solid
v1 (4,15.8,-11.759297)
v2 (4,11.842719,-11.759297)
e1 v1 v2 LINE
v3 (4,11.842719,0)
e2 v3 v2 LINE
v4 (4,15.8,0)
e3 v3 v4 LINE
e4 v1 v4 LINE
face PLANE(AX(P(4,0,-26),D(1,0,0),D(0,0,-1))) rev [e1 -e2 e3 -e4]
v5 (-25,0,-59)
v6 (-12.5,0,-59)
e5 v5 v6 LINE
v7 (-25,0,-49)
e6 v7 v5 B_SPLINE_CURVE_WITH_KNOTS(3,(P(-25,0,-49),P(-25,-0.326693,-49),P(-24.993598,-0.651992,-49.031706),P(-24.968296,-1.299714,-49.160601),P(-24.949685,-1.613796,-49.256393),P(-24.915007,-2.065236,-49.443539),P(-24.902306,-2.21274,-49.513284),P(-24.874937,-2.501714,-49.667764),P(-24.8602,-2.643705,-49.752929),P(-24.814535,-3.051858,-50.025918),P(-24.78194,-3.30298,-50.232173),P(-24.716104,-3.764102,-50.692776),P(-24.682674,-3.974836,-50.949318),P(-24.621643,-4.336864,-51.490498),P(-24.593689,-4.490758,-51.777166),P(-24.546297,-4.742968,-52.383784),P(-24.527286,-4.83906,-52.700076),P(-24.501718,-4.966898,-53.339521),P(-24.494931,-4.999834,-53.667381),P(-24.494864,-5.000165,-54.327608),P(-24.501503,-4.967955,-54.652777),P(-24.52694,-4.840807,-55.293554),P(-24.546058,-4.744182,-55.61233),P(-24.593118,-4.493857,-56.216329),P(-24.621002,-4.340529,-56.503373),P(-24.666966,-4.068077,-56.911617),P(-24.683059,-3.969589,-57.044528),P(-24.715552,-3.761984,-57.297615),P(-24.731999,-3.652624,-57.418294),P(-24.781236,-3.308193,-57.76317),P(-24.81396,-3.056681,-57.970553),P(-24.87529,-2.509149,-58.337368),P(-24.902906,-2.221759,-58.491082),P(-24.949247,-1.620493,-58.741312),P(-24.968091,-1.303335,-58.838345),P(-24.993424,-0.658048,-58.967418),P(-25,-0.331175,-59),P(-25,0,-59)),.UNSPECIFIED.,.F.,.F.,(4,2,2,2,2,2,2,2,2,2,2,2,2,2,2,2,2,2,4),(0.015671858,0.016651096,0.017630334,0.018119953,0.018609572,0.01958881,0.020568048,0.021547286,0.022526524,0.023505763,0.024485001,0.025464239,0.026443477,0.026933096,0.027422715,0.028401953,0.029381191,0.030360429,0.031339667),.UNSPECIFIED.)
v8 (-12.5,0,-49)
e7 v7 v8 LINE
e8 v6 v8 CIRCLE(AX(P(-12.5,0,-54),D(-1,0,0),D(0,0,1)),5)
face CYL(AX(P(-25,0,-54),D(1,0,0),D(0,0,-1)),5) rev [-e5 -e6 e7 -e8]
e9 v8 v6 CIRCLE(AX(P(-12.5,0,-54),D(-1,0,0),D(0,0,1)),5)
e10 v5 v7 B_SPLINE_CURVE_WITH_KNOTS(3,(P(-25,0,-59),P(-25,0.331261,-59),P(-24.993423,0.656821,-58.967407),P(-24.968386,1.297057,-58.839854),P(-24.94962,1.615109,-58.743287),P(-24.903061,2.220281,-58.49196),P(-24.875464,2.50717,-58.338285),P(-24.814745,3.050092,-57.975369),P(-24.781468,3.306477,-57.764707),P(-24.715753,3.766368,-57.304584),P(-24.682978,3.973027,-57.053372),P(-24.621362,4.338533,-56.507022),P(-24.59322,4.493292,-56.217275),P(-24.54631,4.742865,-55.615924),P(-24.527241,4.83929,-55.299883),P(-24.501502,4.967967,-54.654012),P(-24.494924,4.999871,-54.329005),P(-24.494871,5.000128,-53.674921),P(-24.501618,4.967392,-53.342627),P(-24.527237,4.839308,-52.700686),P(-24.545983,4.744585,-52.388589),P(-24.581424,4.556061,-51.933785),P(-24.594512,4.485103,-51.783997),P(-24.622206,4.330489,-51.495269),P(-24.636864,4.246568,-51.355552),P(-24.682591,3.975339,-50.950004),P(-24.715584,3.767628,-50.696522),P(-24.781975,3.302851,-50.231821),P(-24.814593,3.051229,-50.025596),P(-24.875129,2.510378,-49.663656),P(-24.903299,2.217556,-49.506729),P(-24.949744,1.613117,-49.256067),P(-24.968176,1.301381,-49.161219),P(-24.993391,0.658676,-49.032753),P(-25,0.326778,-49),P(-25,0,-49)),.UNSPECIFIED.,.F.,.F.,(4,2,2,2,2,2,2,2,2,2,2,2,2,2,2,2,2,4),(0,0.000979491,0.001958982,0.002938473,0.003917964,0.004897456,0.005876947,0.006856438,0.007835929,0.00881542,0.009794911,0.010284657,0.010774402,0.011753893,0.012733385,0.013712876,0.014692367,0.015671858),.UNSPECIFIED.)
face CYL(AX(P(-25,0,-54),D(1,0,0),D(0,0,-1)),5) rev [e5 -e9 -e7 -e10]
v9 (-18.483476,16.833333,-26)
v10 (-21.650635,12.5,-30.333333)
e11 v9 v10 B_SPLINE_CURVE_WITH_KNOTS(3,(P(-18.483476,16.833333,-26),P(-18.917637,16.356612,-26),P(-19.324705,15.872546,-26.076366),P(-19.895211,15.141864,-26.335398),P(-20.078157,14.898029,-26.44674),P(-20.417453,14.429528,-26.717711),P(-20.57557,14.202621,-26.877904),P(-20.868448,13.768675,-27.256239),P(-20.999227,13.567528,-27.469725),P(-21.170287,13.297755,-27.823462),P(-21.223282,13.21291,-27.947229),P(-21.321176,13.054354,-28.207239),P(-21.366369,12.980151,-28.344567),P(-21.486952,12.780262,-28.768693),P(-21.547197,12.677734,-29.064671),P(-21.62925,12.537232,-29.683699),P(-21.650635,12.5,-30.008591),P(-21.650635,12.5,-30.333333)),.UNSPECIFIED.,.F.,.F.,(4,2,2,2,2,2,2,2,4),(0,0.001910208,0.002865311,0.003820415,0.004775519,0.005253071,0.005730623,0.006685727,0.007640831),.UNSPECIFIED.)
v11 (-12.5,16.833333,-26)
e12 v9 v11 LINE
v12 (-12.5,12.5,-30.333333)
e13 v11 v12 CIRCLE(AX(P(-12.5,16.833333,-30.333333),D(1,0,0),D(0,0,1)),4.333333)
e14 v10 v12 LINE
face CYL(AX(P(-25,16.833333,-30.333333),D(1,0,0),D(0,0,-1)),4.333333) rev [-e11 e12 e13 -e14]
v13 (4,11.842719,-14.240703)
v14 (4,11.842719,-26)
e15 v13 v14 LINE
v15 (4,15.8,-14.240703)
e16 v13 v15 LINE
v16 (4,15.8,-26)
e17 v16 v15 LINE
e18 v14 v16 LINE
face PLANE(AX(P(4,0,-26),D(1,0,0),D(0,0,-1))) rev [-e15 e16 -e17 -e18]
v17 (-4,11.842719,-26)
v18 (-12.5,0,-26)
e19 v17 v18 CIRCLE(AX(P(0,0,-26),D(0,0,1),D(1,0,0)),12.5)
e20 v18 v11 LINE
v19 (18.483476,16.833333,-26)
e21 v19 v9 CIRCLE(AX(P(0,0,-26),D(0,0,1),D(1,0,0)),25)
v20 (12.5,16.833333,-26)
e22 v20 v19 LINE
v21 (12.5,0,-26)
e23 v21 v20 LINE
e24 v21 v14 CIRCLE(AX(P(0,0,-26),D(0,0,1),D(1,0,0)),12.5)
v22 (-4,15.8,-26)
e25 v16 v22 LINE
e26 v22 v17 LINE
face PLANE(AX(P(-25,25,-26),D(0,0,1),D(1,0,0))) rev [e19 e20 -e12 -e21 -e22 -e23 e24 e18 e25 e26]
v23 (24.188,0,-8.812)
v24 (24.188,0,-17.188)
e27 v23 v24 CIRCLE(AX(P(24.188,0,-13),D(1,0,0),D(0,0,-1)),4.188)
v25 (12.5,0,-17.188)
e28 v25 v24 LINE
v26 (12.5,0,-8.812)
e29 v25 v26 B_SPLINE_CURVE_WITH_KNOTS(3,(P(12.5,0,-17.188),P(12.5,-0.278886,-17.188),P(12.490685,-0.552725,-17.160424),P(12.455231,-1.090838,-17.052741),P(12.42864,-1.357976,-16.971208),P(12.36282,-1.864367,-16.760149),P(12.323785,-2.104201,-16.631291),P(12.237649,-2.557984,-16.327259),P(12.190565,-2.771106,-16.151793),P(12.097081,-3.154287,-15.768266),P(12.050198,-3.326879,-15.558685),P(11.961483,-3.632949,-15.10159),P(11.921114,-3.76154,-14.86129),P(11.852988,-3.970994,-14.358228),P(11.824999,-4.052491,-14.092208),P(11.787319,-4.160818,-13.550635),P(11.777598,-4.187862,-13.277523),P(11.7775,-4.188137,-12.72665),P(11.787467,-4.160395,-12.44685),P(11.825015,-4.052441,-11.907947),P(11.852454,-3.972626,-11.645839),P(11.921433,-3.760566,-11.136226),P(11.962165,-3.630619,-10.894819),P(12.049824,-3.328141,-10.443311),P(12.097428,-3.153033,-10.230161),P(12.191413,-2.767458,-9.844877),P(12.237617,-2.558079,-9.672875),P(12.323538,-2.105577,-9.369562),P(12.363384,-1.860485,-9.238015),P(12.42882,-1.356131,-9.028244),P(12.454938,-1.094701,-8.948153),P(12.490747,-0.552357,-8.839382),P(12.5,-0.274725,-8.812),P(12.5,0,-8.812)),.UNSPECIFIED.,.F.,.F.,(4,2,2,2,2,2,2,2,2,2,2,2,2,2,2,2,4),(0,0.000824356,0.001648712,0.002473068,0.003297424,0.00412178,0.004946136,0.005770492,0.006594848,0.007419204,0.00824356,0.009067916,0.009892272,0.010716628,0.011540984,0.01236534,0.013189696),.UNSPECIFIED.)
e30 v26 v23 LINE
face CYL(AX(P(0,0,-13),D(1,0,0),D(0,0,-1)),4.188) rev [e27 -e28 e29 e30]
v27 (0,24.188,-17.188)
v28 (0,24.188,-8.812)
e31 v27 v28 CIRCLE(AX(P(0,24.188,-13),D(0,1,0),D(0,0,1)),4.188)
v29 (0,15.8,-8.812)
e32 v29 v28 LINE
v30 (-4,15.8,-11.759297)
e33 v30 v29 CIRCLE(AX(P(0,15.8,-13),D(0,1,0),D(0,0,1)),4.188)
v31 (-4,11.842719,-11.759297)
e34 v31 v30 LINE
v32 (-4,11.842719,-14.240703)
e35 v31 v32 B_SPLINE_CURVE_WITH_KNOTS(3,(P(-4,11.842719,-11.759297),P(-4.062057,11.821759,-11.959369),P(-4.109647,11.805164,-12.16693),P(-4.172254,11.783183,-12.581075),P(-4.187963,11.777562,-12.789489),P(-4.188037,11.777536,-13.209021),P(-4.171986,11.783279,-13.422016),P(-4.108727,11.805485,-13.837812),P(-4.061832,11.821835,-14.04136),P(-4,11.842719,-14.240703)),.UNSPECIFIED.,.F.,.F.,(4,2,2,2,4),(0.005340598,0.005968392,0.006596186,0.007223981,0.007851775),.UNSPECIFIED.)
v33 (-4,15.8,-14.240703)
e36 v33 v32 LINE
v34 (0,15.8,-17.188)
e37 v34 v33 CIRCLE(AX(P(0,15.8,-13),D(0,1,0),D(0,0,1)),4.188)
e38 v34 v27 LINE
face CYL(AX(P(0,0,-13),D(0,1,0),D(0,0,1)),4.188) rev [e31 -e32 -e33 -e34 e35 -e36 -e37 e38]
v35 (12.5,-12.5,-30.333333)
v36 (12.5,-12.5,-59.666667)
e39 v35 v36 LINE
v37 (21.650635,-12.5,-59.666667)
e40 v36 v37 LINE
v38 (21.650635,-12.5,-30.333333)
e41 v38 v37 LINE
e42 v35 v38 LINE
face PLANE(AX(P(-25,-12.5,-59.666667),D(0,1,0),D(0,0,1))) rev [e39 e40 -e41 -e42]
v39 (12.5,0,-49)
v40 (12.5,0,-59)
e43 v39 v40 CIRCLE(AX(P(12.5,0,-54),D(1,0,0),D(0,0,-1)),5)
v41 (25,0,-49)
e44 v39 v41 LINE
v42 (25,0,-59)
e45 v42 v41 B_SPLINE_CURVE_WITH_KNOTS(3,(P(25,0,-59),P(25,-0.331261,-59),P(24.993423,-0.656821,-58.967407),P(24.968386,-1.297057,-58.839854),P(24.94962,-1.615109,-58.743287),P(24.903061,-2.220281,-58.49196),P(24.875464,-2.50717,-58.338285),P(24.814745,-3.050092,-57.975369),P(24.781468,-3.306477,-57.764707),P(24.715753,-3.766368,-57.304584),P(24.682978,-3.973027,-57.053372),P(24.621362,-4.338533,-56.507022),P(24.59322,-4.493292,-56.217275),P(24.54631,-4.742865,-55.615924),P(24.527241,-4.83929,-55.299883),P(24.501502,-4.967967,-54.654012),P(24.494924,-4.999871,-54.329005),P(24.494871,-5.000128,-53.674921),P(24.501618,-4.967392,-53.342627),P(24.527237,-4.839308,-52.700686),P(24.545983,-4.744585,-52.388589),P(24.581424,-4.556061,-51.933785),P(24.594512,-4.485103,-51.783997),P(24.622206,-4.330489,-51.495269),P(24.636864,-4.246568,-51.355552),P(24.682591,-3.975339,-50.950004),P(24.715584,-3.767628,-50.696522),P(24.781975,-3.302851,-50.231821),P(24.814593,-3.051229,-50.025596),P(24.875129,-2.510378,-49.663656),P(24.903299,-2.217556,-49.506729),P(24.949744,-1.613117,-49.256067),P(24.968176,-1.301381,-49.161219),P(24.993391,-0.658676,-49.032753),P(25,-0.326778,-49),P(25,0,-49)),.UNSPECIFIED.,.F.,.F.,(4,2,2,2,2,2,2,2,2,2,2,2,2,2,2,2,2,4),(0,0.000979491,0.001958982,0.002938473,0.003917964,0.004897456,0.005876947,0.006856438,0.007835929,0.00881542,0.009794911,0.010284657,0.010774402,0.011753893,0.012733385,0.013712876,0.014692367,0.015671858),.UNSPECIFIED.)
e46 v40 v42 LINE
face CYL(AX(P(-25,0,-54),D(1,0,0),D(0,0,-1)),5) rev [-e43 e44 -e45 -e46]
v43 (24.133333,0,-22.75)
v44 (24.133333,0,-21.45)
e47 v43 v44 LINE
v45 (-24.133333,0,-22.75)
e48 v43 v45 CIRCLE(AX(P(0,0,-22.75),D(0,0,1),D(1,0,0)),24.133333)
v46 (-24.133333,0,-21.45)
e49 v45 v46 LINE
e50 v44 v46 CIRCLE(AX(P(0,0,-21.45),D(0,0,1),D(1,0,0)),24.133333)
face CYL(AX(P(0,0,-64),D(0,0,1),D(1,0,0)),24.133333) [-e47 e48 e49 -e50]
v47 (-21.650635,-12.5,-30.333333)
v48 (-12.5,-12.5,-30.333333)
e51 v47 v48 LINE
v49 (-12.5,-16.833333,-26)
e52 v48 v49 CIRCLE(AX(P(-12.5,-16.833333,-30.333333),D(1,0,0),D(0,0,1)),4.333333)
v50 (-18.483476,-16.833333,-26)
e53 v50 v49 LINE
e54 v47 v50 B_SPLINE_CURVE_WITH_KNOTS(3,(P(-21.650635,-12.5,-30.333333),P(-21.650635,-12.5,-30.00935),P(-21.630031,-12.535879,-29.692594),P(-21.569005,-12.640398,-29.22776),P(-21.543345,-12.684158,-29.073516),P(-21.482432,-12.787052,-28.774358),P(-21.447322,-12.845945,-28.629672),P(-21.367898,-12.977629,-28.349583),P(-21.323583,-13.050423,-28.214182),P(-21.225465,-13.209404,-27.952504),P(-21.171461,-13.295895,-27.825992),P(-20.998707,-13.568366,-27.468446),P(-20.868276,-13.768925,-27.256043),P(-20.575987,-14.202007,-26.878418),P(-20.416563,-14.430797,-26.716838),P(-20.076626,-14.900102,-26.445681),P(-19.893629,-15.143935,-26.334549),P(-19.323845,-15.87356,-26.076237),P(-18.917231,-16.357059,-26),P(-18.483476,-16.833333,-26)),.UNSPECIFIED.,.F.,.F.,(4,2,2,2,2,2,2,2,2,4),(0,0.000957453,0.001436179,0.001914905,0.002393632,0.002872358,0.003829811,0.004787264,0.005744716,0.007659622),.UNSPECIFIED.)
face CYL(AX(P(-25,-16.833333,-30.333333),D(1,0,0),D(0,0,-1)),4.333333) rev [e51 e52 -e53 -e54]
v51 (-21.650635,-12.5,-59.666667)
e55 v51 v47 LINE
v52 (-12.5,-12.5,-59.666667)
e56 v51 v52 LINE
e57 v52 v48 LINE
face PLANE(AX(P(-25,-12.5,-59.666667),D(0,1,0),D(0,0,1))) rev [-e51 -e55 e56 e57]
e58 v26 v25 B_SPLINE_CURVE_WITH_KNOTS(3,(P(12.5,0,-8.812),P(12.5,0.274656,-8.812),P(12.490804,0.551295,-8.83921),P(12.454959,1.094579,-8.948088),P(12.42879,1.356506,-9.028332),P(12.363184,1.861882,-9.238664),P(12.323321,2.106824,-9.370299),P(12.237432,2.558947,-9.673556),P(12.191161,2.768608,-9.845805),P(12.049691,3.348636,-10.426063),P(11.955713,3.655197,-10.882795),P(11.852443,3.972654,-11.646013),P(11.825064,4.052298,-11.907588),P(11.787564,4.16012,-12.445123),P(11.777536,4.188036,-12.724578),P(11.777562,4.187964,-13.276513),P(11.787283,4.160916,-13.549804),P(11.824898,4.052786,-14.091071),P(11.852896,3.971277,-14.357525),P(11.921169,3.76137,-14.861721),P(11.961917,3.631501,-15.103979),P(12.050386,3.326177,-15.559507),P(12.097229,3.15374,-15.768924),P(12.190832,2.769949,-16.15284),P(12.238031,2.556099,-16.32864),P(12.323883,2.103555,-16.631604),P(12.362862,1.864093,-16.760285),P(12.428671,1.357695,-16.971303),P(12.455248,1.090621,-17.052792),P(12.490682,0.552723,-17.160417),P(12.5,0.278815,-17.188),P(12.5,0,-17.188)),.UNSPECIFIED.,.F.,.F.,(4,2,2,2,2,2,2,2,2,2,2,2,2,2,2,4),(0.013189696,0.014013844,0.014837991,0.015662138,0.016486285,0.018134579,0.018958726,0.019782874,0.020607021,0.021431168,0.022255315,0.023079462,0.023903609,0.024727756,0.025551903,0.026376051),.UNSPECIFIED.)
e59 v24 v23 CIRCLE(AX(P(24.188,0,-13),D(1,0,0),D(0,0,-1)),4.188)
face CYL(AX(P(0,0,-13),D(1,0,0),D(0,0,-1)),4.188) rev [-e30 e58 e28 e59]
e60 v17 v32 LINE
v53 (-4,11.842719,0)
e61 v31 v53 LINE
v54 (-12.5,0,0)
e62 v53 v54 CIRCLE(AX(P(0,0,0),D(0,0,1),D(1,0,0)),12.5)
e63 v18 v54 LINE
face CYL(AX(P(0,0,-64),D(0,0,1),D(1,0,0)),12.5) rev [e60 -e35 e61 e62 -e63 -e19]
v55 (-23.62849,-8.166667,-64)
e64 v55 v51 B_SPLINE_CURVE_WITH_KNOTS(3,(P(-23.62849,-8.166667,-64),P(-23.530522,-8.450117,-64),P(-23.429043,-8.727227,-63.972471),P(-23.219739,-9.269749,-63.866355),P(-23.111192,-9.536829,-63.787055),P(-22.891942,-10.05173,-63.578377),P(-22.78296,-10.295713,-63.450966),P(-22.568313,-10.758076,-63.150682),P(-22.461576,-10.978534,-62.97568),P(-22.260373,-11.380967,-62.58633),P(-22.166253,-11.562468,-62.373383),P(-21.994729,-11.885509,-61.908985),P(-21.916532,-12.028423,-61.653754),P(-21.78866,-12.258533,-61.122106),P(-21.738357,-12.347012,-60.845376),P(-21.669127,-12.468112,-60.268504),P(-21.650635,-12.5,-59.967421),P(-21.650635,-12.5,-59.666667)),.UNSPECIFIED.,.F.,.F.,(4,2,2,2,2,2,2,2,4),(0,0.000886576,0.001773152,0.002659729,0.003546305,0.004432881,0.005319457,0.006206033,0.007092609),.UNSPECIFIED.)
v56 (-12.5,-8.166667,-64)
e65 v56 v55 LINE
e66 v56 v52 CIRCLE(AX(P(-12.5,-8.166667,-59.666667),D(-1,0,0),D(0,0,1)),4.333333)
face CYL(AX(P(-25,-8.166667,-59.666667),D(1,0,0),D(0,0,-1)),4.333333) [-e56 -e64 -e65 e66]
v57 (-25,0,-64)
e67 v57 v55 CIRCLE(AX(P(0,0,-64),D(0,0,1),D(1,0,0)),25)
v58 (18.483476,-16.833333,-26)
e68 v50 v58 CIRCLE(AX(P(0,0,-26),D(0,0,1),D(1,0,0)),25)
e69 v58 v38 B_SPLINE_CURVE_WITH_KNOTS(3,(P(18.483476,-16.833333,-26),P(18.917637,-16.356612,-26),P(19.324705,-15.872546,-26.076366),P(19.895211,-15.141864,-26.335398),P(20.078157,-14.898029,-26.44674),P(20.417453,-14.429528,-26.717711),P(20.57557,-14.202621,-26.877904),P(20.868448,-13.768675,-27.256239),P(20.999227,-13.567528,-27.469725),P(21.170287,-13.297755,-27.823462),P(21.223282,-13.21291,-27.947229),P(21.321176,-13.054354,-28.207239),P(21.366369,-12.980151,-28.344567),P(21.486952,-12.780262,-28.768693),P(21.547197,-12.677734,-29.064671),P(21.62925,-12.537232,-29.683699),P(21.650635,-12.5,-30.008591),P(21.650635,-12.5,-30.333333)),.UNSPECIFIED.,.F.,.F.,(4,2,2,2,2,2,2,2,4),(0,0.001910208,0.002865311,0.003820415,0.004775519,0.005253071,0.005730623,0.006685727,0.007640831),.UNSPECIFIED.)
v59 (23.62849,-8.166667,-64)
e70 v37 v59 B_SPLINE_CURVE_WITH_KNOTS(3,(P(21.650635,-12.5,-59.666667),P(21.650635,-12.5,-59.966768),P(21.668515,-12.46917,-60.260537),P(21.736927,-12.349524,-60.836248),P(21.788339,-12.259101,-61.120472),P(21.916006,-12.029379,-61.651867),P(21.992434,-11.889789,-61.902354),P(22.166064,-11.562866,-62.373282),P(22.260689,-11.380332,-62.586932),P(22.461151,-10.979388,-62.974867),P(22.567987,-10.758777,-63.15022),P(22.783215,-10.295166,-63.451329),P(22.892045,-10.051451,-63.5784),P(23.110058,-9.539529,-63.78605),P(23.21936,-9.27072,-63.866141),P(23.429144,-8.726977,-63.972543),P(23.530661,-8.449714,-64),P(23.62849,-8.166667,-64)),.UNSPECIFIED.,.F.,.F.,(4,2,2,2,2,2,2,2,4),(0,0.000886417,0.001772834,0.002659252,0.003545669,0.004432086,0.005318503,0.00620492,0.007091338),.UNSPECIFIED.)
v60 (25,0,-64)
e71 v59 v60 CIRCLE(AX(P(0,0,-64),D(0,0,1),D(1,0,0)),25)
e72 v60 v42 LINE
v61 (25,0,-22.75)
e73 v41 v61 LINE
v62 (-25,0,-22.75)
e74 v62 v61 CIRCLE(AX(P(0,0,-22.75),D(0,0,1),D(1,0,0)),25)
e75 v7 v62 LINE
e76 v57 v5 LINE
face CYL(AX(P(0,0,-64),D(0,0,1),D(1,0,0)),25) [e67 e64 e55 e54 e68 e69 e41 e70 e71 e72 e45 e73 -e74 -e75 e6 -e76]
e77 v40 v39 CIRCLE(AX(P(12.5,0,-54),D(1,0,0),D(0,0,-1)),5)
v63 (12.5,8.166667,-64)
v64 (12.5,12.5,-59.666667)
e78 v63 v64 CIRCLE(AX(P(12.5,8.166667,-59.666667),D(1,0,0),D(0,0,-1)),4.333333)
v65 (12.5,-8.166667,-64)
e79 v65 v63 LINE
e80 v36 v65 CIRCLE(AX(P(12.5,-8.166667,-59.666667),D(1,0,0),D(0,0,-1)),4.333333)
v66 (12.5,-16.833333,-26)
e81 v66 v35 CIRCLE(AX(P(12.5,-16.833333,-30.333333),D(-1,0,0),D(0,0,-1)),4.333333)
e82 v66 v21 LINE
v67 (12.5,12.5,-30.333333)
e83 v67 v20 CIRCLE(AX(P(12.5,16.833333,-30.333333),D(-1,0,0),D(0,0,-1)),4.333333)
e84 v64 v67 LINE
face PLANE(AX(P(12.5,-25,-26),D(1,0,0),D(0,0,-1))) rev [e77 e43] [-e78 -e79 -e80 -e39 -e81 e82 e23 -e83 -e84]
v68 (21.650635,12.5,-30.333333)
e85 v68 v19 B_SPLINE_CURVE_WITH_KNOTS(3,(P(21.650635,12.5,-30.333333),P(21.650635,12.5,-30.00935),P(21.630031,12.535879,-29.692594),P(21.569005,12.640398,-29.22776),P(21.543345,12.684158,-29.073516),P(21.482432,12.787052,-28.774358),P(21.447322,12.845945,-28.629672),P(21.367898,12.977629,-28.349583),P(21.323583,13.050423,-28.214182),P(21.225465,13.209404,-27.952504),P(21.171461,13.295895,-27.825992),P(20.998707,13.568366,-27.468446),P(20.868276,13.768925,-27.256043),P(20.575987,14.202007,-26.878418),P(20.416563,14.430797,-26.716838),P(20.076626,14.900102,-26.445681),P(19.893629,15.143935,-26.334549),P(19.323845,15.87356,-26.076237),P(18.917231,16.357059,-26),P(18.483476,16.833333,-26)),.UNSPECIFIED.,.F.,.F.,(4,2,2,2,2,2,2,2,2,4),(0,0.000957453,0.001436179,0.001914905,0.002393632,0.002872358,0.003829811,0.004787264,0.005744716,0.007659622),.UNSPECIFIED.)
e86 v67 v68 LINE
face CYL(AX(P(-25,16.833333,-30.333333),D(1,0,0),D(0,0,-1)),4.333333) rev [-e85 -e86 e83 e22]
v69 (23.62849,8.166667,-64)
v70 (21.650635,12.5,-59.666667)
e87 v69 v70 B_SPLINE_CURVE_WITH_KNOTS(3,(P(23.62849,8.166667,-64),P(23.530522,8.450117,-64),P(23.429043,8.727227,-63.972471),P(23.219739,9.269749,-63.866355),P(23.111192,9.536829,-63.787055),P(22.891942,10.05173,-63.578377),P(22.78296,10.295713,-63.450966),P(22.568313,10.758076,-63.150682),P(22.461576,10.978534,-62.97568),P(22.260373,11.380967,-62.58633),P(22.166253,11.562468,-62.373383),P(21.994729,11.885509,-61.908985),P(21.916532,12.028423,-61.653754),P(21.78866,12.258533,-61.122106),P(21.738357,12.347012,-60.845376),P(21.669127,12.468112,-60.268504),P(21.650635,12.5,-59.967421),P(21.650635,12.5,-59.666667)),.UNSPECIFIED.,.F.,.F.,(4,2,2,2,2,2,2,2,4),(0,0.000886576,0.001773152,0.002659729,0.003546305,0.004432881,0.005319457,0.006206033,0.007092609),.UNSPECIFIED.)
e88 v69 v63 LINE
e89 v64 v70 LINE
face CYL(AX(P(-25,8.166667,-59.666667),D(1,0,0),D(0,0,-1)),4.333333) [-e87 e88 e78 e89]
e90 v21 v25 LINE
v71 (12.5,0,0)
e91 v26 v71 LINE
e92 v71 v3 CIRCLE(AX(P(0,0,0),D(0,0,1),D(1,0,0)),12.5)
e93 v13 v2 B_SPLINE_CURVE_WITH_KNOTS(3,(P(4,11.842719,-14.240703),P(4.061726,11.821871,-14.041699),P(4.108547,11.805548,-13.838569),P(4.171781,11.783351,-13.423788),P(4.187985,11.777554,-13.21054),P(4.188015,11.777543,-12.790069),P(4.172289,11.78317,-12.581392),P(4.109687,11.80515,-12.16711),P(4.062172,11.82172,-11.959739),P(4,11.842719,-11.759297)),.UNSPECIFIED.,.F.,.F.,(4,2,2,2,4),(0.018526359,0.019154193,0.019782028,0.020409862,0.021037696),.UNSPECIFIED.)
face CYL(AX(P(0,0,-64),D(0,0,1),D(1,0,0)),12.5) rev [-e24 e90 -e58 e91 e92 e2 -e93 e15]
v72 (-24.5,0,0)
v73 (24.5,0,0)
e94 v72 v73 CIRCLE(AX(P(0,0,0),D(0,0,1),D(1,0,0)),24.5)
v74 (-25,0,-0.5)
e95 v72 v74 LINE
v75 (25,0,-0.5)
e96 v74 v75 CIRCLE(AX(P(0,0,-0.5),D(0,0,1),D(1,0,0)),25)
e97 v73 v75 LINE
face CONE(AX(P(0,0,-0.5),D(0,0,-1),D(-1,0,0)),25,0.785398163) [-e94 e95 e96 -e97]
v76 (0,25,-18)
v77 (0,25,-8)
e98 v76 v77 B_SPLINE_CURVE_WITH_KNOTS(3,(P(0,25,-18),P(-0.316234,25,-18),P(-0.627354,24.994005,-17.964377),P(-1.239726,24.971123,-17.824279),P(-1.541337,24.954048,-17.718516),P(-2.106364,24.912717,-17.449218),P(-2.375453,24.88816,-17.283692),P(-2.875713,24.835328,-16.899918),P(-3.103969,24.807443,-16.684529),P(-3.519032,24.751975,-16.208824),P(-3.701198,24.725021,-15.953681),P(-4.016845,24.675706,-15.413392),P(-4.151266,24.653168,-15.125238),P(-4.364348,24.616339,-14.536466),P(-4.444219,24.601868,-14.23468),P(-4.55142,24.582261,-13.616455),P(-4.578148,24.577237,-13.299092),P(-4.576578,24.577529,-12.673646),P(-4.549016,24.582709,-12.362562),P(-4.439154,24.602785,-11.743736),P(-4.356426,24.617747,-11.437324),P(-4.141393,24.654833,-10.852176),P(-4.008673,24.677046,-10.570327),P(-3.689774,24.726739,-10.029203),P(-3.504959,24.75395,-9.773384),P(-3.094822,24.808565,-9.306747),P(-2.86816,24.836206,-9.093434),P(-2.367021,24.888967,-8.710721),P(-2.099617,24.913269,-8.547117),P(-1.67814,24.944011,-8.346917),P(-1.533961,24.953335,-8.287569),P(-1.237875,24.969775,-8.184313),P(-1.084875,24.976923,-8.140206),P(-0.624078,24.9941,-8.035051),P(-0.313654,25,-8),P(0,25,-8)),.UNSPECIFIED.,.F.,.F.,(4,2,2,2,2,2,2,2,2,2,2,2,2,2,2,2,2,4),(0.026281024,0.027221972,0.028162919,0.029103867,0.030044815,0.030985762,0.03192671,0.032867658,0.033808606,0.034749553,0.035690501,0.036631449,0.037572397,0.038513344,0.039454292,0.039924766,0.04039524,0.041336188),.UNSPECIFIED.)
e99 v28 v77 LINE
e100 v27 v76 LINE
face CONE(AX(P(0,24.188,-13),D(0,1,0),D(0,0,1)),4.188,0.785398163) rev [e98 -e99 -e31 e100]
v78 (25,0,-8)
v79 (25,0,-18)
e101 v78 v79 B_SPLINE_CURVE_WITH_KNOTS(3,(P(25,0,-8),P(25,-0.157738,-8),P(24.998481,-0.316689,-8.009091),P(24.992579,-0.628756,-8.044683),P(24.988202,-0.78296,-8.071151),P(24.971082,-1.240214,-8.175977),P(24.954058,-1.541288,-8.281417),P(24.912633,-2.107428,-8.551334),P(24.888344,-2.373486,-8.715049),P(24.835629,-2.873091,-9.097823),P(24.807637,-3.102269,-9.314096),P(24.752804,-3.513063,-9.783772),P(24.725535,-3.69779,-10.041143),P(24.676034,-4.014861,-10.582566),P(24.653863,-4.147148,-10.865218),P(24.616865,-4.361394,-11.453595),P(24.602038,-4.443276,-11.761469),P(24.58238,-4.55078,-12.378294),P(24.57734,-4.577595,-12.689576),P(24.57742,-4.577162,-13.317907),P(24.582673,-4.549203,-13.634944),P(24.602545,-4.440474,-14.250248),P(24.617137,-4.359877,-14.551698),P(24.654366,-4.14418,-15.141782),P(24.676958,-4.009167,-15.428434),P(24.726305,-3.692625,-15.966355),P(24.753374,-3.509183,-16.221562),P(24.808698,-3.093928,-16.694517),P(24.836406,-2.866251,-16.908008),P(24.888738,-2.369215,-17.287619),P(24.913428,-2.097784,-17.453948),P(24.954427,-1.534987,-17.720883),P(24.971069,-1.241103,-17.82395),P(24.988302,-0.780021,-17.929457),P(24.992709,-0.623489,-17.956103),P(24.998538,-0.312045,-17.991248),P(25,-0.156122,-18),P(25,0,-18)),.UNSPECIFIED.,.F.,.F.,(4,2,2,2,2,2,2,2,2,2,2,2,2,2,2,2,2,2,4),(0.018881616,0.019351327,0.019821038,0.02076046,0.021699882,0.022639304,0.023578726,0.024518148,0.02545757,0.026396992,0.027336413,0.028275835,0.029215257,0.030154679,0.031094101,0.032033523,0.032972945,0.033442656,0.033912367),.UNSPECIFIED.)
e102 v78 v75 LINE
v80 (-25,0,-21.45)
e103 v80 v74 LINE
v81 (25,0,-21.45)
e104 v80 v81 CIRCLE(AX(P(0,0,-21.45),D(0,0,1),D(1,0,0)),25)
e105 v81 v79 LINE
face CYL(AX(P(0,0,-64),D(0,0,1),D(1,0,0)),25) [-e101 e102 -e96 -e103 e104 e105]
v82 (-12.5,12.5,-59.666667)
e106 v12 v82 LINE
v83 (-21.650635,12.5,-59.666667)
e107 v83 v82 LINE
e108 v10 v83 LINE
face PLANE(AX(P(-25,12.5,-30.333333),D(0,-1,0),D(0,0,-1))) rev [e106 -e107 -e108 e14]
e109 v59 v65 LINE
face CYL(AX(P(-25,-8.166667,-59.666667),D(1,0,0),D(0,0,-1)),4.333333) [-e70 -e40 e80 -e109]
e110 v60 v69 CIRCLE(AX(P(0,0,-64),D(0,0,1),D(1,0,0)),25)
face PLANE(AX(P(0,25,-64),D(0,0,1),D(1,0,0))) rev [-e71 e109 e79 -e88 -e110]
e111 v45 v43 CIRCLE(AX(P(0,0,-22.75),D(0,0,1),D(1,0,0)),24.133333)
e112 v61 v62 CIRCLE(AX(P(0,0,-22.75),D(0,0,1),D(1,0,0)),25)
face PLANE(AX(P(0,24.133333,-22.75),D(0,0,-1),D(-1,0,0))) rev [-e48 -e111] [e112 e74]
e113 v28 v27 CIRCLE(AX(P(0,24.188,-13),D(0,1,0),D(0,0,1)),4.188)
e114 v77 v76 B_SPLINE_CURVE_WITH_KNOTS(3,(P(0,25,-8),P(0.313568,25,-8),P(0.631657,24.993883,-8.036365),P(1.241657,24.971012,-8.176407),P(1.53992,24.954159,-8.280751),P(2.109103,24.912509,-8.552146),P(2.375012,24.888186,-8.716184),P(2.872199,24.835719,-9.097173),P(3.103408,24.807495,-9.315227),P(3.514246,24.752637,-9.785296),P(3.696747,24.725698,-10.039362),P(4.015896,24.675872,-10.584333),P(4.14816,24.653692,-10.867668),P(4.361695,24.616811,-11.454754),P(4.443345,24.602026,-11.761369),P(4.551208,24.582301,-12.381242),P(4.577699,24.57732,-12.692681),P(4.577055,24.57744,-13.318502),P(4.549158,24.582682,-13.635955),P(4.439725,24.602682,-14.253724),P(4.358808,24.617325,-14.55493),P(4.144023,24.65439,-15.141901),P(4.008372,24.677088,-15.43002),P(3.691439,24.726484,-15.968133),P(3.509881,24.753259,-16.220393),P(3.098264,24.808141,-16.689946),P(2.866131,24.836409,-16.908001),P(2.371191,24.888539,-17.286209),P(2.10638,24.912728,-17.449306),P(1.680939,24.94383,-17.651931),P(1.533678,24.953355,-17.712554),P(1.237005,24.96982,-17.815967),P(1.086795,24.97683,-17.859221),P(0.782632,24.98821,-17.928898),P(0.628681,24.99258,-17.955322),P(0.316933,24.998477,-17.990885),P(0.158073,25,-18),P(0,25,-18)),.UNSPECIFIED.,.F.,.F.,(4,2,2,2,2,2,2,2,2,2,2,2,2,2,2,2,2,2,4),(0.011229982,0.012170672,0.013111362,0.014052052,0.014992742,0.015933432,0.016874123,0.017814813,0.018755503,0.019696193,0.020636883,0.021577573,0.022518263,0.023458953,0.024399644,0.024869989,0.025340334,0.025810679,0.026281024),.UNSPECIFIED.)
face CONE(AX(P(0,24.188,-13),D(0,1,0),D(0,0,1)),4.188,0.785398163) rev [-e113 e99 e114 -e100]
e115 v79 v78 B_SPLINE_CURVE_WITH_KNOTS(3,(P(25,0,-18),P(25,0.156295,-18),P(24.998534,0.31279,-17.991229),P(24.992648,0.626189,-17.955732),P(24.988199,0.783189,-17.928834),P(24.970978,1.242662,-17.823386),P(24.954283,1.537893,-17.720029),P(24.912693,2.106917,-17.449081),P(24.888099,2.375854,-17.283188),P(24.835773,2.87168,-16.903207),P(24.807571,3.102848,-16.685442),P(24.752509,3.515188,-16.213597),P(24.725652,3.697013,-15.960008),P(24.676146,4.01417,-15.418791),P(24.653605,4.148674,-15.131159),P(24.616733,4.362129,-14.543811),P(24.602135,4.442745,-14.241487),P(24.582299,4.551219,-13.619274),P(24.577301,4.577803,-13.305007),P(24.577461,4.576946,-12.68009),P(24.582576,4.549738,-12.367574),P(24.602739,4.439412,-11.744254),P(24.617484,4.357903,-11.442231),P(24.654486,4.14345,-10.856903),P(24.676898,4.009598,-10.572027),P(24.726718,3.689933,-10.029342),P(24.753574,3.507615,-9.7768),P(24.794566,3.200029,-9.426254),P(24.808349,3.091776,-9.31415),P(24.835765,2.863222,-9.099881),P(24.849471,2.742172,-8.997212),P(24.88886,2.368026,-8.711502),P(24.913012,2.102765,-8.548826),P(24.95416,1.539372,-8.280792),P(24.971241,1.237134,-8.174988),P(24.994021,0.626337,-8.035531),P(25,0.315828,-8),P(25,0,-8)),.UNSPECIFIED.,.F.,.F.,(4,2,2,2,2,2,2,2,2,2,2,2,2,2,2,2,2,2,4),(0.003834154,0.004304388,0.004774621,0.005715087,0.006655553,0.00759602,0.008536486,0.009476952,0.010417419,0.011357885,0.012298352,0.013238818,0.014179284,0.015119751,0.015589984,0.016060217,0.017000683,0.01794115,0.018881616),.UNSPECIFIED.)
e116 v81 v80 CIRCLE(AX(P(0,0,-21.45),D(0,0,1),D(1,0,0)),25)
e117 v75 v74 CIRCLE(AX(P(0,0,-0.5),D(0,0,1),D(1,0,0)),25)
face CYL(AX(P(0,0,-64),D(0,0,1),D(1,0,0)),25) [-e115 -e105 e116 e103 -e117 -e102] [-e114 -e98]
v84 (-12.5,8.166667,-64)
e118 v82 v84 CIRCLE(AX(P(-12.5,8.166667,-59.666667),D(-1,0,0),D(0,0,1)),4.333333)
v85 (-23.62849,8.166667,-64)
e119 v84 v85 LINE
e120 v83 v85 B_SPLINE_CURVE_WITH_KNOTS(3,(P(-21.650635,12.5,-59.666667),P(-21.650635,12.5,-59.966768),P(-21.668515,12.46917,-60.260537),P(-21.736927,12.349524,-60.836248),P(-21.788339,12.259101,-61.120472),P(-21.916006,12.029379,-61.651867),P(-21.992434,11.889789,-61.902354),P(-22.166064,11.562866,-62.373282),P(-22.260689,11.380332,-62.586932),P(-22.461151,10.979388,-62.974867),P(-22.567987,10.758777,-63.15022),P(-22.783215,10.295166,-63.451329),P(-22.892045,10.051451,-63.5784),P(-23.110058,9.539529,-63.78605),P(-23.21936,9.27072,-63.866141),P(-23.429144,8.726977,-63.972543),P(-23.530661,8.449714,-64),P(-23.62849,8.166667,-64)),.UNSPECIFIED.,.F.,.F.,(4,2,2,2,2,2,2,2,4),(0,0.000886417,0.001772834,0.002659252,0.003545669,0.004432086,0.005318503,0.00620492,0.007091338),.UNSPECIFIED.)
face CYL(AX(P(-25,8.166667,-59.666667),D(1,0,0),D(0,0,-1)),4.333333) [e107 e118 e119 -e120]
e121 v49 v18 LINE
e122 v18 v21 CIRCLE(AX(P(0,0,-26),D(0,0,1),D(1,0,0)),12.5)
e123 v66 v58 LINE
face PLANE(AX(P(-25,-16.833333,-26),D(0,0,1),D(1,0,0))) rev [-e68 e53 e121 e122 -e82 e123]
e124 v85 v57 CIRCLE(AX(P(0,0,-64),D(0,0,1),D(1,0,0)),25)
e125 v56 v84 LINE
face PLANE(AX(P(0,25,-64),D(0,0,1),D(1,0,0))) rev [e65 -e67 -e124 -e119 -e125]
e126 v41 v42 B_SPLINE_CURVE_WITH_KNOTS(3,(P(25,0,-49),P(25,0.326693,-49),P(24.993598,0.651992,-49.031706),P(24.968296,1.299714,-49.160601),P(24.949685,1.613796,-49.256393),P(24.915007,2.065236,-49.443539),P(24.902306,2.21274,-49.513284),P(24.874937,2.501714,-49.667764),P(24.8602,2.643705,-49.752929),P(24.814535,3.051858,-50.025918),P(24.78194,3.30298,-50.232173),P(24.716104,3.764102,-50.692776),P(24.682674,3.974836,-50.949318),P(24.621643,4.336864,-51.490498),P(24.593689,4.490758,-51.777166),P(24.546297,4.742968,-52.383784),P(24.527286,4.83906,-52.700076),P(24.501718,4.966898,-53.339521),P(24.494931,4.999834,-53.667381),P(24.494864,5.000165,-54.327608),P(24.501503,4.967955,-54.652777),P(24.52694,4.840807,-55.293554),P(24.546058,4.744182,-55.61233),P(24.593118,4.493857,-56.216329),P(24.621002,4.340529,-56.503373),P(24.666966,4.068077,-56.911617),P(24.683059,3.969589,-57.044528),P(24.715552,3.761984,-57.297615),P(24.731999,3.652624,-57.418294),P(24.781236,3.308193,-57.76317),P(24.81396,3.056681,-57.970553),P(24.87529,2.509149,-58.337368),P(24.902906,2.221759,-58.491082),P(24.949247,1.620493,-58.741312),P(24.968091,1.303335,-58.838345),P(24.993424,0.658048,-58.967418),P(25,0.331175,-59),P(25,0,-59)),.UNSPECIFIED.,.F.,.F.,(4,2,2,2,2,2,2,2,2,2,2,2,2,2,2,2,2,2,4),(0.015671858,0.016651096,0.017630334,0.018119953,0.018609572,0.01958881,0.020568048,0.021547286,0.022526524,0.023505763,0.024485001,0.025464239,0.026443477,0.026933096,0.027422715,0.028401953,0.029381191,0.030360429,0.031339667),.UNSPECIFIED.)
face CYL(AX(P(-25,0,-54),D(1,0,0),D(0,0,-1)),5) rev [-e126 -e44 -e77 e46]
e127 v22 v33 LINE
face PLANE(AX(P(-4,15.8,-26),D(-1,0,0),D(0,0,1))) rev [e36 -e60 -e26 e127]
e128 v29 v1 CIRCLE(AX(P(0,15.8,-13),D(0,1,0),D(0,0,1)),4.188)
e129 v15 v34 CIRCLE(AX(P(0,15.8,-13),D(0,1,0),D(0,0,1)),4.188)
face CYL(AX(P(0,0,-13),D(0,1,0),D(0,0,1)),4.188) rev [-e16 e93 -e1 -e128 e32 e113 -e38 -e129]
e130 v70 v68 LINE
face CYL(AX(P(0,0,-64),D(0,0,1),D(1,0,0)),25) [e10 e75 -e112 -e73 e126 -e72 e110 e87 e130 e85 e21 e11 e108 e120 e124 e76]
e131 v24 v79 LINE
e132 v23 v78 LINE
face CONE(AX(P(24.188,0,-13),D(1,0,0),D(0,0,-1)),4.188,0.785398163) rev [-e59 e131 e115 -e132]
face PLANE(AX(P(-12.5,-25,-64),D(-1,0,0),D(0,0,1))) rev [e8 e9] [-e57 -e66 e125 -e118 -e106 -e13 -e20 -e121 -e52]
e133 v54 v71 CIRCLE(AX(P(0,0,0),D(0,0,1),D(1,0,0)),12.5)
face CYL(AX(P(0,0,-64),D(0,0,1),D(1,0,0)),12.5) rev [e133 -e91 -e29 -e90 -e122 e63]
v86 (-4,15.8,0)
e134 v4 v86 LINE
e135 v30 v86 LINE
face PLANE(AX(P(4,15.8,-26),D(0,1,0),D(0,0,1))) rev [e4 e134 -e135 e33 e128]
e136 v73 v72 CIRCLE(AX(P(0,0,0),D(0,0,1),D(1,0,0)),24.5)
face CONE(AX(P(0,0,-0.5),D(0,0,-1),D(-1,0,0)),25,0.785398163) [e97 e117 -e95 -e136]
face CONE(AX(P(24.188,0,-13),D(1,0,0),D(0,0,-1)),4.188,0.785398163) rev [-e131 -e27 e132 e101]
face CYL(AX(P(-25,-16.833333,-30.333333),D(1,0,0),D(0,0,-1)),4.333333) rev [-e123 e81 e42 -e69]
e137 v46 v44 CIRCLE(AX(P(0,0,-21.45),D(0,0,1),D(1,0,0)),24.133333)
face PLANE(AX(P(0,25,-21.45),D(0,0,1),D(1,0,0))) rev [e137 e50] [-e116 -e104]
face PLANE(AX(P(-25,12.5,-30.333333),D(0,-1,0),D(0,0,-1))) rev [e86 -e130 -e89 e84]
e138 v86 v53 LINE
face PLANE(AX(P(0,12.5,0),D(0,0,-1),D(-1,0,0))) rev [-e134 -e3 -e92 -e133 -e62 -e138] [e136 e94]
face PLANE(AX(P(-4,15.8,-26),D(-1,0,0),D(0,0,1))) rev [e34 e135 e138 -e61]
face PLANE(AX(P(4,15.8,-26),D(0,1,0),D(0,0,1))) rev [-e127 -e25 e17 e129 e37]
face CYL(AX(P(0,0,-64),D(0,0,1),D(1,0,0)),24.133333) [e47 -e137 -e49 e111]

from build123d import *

# Parameters (mm, degrees)
CUT_EXTRUDE_1_DEPTH      = 25
CUT_EXTRUDE_1_DEPTH_BACK = 25
CUT_EXTRUDE_2_DEPTH      = 25
CUT_EXTRUDE_2_DEPTH_BACK = 25
SKETCH_3_W               = 25
SKETCH_3_H               = 38
CUT_EXTRUDE_3_DEPTH      = 25
CUT_EXTRUDE_3_DEPTH_BACK = 25
SKETCH_4_R               = 5
SKETCH_7_W               = 8
SKETCH_7_H               = 15.8
CUT_EXTRUDE_4_DEPTH      = 26


with BuildPart() as part:
    # 草图1 → 旋转1 (revolve)
    with BuildSketch(Plane(origin=(0, 0, 0), x_dir=(0, 0, -1), z_dir=(1, 0, 0)), mode=Mode.PRIVATE) as revolve_1_sk:
        Polygon((26, 0), (26, 12.5), (0, 12.5), (0, 24.5), (0.5, 25), (21.45, 25), (21.45, 24.133333333), (22.75, 24.133333333), (22.75, 25), (64, 25), (64, 0), align=None)
    revolve(revolve_1_sk.sketch.rotate(Axis((0, 0, -64), (0, 0, 1)), 270), axis=Axis((0, 0, -64), (0, 0, 1)))

    # 草图2 → 切除-拉伸1 (cut, two sides: drawn at the far end of the back side and taken through both)
    with BuildSketch(Plane(origin=(0, 0, 0), x_dir=(0, 0, -1), z_dir=(1, 0, 0)).offset(-CUT_EXTRUDE_1_DEPTH_BACK)):
        with BuildLine():
            Line((30.333333333, 12.5), (59.666666667, 12.5))
            ThreePointArc((59.666666667, 12.5), (62.730796052, 11.230796052), (64, 8.166666667))
            Line((64, 8.166666667), (64, -8.166666667))
            ThreePointArc((64, -8.166666667), (62.730796052, -11.230796052), (59.666666667, -12.5))
            Line((59.666666667, -12.5), (30.333333333, -12.5))
            ThreePointArc((30.333333333, -12.5), (27.269203948, -13.769203948), (26, -16.833333333))
            Line((26, -16.833333333), (26, -25))
            Line((26, -25), (69, -25))
            Line((69, -25), (69, 25))
            Line((69, 25), (26, 25))
            Line((26, 25), (26, 16.833333333))
            ThreePointArc((26, 16.833333333), (27.269203948, 13.769203948), (30.333333333, 12.5))
        make_face()
    extrude(amount=CUT_EXTRUDE_1_DEPTH + CUT_EXTRUDE_1_DEPTH_BACK, mode=Mode.SUBTRACT)

    # 草图3 → 切除-拉伸2 (cut, two sides: drawn at the far end of the back side and taken through both)
    with BuildSketch(Plane(origin=(0, 0, 0), x_dir=(1, 0, 0), z_dir=(0, 1, 0)).offset(-CUT_EXTRUDE_2_DEPTH_BACK)):
        with Locations((0, 45)):
            Rectangle(SKETCH_3_W, SKETCH_3_H)
    extrude(amount=CUT_EXTRUDE_2_DEPTH + CUT_EXTRUDE_2_DEPTH_BACK, mode=Mode.SUBTRACT)

    # 草图4 → 切除-拉伸3 (cut, two sides: drawn at the far end of the back side and taken through both)
    with BuildSketch(Plane(origin=(0, 0, 0), x_dir=(0, 0, -1), z_dir=(1, 0, 0)).offset(-CUT_EXTRUDE_3_DEPTH_BACK)):
        with Locations((54, 0)):
            Circle(SKETCH_4_R)
    extrude(amount=CUT_EXTRUDE_3_DEPTH + CUT_EXTRUDE_3_DEPTH_BACK, mode=Mode.SUBTRACT)

    # 草图5 → 切除-旋转1 (revolve, cut)
    with BuildSketch(Plane(origin=(0, 0, 0), x_dir=(0, 0, -1), z_dir=(1, 0, 0)), mode=Mode.PRIVATE) as cut_revolve_1_sk:
        Polygon((13, 25), (18, 25), (17.188, 24.188), (17.188, 0), (13, 0), align=None)
    revolve(cut_revolve_1_sk.sketch.rotate(Axis((0, 0, -13), (0, 1, 0)), 180), axis=Axis((0, 0, -13), (0, 1, 0)), mode=Mode.SUBTRACT)

    # 草图6 → 切除-旋转2 (revolve, cut)
    with BuildSketch(Plane(origin=(0, 0, 0), x_dir=(1, 0, 0), z_dir=(0, 1, 0)), mode=Mode.PRIVATE) as cut_revolve_2_sk:
        Polygon((25, 13), (25, 8), (24.188, 8.812), (0, 8.812), (0, 13), align=None)
    revolve(cut_revolve_2_sk.sketch.rotate(Axis((0, 0, -13), (1, 0, 0)), 180), axis=Axis((0, 0, -13), (1, 0, 0)), mode=Mode.SUBTRACT)

    # 草图7 → 切除-拉伸4 (cut)
    with BuildSketch(Plane.XY):
        with Locations((0, 7.9)):
            Rectangle(SKETCH_7_W, SKETCH_7_H)
    extrude(amount=-CUT_EXTRUDE_4_DEPTH, mode=Mode.SUBTRACT)


solid = part.part
